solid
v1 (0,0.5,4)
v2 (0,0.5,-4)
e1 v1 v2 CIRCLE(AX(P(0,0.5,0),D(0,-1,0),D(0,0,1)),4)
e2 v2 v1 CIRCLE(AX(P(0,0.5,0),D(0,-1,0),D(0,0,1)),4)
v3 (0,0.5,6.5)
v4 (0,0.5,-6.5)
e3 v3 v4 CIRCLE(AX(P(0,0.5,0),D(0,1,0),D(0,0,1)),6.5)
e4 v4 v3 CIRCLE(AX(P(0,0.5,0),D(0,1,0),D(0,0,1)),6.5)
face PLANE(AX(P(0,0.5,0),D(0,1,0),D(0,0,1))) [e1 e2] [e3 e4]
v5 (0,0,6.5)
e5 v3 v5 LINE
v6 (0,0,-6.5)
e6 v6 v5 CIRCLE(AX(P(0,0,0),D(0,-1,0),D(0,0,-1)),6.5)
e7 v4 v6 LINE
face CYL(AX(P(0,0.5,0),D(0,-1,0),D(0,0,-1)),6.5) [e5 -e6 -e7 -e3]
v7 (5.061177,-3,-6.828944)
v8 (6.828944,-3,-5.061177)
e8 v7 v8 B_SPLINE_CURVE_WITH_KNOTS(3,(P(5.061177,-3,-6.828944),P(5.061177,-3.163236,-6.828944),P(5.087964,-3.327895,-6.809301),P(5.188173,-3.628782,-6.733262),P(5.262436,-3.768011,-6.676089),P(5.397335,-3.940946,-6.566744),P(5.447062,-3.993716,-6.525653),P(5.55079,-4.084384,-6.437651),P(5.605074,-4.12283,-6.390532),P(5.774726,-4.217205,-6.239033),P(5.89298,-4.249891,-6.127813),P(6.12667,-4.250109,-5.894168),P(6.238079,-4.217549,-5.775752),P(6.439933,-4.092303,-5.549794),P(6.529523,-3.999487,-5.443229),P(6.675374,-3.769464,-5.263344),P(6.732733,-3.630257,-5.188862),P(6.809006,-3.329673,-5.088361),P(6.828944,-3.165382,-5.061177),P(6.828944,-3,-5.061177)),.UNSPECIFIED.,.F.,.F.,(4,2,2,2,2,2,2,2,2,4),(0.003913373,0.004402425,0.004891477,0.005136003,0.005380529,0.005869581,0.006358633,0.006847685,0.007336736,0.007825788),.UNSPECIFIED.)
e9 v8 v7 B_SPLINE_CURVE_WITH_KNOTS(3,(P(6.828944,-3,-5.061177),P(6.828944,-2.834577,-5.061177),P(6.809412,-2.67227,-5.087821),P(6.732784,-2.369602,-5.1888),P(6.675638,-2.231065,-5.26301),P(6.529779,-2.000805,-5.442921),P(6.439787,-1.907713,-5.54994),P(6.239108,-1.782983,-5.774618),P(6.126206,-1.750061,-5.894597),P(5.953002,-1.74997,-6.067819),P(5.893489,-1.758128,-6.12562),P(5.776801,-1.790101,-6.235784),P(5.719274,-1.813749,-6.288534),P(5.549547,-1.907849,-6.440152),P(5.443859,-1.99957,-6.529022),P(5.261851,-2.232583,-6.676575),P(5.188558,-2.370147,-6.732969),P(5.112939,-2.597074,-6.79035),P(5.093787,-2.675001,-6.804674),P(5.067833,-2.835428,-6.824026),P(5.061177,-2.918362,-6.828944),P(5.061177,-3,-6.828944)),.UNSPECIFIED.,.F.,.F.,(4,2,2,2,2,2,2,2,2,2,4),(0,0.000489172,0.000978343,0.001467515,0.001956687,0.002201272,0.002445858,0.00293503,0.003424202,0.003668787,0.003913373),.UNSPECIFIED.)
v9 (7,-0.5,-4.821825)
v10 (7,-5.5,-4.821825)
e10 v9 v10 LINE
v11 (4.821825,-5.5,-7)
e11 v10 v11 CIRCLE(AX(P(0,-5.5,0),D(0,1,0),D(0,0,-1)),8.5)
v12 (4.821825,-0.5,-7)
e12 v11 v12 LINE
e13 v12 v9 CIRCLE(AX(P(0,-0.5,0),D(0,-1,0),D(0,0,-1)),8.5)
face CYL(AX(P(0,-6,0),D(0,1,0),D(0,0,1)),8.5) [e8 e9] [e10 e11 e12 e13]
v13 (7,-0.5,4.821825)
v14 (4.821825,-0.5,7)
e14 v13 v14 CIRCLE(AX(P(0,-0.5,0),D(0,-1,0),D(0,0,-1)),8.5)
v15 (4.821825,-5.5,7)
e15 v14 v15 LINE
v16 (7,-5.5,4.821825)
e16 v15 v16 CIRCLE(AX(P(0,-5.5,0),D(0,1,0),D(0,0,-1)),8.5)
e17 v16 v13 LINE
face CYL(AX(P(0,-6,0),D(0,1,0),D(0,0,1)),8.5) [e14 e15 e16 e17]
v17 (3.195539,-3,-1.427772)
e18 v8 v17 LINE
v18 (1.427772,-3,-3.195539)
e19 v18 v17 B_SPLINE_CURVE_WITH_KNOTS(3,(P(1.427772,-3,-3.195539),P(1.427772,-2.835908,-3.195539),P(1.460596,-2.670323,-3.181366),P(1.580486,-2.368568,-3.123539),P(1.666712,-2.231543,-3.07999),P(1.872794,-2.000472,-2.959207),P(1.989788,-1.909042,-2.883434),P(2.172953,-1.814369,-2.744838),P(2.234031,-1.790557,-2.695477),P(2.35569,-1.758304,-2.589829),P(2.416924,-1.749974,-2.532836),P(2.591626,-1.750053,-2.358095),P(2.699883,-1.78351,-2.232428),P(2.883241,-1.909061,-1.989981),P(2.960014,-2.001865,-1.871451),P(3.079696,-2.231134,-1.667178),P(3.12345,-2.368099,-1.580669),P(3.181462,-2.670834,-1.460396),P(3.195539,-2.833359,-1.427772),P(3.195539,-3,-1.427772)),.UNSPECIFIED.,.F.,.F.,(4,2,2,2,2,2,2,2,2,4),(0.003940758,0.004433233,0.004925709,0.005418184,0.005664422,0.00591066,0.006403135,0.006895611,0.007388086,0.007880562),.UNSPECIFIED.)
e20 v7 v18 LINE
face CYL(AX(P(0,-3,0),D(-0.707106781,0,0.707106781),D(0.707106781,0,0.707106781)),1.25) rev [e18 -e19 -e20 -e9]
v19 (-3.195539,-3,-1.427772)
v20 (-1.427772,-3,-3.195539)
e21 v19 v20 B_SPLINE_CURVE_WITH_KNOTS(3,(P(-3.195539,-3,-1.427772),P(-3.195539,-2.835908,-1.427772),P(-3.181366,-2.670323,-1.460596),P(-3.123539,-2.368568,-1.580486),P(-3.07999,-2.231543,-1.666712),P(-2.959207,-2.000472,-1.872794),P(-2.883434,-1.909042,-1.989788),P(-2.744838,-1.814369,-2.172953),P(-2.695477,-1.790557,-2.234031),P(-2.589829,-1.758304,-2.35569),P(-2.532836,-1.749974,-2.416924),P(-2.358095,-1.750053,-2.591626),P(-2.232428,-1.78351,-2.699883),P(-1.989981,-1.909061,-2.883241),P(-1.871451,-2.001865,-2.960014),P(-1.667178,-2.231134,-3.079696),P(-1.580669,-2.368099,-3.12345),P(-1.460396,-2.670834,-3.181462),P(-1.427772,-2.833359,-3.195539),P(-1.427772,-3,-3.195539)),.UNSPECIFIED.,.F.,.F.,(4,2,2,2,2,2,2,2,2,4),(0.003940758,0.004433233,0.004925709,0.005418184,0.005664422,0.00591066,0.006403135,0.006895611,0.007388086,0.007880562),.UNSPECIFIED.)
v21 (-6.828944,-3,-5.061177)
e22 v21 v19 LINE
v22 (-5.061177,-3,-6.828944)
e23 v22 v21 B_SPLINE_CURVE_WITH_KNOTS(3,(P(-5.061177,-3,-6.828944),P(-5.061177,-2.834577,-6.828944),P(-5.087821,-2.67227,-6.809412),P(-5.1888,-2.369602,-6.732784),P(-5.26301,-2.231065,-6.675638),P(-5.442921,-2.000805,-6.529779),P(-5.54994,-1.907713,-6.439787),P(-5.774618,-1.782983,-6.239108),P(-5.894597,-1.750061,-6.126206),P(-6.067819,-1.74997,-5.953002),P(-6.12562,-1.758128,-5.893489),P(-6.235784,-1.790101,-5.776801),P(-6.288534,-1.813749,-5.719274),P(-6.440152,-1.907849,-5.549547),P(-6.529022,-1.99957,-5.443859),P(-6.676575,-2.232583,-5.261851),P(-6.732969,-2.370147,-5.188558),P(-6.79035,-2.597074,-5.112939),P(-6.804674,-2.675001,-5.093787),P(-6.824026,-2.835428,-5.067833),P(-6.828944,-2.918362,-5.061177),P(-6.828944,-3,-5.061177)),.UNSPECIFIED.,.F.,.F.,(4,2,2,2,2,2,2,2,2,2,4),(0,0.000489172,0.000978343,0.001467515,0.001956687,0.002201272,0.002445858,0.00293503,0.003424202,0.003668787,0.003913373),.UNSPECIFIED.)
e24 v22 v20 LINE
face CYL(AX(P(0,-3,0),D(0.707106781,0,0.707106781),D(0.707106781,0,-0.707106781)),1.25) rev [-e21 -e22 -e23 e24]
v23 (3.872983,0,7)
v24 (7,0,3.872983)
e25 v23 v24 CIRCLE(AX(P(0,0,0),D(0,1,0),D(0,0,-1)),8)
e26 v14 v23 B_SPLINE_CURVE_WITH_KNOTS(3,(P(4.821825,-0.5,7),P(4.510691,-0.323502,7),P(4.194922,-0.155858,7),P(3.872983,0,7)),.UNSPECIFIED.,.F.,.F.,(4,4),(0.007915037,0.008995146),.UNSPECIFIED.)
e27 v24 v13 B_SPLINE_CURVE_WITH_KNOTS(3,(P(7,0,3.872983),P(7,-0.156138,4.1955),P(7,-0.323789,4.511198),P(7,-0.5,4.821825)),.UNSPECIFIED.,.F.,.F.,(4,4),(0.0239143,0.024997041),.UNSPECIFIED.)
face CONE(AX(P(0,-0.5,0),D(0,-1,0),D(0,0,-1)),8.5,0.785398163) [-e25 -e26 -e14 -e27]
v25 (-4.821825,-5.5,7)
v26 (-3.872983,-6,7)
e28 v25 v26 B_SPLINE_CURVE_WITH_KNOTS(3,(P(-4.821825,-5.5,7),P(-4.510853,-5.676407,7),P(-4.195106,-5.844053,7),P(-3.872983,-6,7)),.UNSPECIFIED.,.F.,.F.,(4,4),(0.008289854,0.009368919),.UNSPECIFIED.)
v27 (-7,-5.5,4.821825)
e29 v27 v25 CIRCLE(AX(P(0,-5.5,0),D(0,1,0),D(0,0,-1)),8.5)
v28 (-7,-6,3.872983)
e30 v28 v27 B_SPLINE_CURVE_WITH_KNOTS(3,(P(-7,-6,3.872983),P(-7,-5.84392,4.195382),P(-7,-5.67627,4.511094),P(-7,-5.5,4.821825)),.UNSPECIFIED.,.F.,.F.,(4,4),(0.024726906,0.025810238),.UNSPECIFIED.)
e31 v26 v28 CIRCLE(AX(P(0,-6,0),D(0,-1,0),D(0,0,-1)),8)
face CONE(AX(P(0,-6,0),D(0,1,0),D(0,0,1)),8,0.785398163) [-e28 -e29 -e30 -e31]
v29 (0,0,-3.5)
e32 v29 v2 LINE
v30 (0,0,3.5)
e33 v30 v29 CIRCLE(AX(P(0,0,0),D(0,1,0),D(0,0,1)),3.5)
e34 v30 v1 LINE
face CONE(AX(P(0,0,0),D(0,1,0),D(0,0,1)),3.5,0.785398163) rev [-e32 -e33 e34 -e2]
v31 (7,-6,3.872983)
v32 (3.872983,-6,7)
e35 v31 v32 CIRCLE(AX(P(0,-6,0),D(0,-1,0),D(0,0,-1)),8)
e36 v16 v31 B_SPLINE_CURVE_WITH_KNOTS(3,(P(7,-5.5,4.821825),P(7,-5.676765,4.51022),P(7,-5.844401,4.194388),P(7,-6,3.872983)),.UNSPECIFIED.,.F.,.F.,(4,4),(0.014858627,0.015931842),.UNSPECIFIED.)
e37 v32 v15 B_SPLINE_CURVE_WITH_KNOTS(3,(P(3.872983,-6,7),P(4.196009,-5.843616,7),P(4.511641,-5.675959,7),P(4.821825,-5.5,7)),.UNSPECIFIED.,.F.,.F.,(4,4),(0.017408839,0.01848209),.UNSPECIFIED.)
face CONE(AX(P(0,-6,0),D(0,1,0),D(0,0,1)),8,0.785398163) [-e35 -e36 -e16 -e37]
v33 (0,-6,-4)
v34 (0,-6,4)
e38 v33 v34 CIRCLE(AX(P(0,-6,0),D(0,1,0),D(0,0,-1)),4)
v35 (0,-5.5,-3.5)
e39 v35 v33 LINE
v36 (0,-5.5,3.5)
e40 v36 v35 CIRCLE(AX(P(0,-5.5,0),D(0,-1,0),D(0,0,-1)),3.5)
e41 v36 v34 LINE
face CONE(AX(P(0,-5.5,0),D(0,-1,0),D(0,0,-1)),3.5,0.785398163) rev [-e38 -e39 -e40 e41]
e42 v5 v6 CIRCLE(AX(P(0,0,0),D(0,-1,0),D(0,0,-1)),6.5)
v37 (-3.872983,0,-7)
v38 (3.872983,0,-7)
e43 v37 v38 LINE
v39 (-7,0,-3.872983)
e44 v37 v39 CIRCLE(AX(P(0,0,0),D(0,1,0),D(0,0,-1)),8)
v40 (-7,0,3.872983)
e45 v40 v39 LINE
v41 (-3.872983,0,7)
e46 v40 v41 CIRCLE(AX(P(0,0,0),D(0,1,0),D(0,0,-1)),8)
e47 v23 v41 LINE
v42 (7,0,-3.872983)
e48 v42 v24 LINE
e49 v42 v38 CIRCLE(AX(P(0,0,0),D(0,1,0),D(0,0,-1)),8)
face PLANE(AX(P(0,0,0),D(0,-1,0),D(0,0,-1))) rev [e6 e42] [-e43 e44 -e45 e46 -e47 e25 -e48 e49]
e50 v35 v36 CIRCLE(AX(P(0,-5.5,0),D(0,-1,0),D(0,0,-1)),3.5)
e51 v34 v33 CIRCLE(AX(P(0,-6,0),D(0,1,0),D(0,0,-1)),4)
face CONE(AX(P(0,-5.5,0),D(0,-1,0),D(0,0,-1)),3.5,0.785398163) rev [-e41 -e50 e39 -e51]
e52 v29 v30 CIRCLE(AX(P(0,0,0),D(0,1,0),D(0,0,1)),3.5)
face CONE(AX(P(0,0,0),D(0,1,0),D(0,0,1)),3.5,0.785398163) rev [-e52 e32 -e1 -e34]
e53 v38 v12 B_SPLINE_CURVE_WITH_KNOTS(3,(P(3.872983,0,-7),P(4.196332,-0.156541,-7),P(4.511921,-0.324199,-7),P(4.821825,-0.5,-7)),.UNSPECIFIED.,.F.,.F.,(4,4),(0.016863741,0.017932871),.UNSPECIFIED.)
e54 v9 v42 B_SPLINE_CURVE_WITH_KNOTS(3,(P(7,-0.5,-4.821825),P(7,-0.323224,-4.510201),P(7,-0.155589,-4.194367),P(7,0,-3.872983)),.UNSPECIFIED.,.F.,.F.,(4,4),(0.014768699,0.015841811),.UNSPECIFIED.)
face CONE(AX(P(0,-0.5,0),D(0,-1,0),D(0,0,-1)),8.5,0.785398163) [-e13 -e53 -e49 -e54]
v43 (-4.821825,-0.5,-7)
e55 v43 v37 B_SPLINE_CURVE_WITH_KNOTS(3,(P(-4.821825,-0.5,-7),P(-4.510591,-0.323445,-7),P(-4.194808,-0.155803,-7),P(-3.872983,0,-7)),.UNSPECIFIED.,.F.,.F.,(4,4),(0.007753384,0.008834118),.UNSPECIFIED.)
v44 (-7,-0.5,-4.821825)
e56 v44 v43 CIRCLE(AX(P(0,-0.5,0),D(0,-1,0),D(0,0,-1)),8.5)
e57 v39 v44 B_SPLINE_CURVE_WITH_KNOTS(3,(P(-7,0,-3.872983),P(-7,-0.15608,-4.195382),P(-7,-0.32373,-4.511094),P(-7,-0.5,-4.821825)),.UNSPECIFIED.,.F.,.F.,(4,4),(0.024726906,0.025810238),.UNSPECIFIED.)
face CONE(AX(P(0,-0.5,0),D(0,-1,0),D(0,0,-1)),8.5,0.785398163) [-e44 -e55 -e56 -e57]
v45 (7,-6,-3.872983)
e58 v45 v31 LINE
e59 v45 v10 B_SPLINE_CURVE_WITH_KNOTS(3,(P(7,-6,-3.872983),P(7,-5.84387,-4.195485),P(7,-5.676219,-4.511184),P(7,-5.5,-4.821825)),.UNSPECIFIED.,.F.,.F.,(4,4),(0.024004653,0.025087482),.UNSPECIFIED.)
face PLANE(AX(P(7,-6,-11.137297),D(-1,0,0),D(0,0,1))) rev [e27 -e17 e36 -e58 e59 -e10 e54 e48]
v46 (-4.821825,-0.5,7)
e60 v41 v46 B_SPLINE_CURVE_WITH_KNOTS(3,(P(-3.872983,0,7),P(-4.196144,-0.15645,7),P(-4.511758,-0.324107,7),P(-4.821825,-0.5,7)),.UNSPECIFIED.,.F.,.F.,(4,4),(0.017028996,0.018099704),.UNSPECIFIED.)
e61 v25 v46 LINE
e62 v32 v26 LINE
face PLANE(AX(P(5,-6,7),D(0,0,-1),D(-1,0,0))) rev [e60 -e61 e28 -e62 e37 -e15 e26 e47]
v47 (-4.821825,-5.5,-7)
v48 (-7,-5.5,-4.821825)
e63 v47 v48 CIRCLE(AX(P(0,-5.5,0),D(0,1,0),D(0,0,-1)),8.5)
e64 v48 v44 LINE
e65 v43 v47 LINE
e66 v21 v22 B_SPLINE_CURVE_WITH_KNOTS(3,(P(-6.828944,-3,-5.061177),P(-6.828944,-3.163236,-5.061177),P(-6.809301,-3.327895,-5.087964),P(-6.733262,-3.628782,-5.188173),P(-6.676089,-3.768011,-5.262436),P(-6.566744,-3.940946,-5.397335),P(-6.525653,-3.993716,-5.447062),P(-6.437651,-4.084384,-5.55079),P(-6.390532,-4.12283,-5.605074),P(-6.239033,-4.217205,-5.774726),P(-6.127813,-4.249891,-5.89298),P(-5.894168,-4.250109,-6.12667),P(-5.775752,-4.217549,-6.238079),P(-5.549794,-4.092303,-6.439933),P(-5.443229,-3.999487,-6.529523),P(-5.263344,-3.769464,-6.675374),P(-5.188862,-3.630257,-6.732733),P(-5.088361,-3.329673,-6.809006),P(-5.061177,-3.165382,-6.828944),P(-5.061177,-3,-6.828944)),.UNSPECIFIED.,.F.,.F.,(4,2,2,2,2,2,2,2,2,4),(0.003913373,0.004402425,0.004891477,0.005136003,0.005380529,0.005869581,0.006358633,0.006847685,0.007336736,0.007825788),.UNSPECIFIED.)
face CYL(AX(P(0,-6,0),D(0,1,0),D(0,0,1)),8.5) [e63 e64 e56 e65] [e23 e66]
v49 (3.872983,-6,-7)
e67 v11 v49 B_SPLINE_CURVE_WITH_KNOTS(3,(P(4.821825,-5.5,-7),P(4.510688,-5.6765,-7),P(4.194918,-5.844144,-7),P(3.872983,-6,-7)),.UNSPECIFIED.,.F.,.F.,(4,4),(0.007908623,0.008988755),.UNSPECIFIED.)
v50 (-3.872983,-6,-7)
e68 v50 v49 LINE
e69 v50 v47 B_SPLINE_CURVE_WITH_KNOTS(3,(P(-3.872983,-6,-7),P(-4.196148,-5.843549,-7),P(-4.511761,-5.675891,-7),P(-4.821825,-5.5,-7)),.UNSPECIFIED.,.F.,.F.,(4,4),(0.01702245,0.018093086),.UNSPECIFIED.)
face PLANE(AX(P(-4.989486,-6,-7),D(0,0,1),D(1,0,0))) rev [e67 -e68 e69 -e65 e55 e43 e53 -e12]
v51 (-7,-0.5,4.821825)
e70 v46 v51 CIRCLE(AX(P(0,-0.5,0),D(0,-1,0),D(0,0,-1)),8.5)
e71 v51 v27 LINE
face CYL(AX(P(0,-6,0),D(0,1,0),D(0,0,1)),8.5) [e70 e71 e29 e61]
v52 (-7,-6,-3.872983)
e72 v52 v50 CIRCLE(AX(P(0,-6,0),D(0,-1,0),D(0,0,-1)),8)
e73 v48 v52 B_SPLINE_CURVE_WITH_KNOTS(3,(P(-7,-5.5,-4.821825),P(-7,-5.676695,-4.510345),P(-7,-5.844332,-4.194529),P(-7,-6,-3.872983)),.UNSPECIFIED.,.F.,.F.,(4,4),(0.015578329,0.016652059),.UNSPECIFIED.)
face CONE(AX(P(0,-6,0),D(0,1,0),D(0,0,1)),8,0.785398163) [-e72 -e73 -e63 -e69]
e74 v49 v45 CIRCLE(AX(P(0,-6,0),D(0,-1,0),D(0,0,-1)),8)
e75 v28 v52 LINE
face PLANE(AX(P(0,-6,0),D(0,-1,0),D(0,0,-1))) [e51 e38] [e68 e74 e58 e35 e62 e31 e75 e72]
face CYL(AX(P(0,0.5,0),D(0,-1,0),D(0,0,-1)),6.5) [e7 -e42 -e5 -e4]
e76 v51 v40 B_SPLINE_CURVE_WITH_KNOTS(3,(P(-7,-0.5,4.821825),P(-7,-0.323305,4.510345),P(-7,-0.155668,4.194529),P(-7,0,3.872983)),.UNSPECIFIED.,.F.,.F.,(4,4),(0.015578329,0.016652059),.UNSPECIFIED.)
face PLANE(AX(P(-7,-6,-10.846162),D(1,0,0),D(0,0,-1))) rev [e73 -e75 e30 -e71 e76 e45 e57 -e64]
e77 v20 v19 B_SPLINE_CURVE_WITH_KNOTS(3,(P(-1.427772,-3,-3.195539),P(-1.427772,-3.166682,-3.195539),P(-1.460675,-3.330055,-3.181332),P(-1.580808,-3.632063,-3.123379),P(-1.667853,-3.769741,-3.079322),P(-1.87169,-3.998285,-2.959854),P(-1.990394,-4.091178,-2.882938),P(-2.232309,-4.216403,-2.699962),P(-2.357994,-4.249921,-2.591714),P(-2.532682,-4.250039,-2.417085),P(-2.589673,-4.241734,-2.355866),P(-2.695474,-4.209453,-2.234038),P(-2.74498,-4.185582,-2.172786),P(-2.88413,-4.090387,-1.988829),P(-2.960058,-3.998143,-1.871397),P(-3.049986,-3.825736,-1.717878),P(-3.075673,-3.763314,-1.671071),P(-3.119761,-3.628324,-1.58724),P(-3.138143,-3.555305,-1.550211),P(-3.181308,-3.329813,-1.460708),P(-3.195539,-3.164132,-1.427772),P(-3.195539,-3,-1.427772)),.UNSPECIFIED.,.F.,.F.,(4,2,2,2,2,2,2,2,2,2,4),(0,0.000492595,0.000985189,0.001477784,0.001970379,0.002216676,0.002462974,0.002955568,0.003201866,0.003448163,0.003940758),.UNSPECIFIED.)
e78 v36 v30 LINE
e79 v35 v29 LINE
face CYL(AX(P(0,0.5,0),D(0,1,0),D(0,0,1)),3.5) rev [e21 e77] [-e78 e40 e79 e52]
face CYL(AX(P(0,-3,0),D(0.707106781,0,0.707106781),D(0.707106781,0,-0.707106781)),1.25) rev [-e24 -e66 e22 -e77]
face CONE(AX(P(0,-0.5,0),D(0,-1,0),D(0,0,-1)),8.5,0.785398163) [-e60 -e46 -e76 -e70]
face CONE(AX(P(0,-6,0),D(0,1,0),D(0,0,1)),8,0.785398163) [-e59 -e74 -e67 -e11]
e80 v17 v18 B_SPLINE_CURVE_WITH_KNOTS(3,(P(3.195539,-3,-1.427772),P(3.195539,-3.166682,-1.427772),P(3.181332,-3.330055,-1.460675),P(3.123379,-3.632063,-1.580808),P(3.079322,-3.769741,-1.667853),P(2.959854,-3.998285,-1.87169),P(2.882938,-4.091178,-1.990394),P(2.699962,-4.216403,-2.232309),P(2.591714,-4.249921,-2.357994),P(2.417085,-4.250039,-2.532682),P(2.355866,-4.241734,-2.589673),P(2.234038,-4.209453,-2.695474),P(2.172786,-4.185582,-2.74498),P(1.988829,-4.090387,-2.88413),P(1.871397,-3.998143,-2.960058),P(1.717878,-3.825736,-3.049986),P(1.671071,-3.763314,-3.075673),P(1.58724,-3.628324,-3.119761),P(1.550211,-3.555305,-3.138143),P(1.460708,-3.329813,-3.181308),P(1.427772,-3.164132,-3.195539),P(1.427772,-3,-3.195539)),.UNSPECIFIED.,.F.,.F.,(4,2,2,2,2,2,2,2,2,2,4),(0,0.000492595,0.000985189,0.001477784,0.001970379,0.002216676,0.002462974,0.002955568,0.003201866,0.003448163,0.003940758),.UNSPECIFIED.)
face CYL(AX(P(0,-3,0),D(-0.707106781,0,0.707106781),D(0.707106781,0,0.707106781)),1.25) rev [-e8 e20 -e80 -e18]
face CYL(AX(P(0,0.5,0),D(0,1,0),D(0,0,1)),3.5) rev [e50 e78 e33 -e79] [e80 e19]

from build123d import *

# Parameters (mm, degrees)
SKETCH1_R                 = 6.5
BOSS_EXTRUDE1_DEPTH       = 0.5
SKETCH3_R                 = 8.5
BOSS_EXTRUDE3_DEPTH       = 6
CHAMFER2_SIZE             = 0.5
SKETCH4_W                 = 4.01520781
SKETCH4_H                 = 18.659876277
SKETCH4_W_2               = 10.097066699
SKETCH4_H_2               = 2.598075642
SKETCH4_W_3               = 5.358269855
SKETCH4_H_3               = 23.485379118
SKETCH4_W_4               = 10.284722044
SKETCH4_H_4               = 2.952358684
CUT_EXTRUDE3_DEPTH        = 14.435028843
M8X1_0_TAPPED_HOLE1_D     = 7
M8X1_0_TAPPED_HOLE1_DEPTH = 19
M8X1_0_TAPPED_HOLE1_TIP   = 2.103012167
SKETCH7_W                 = 1.25
SKETCH7_H                 = 9.899494937
CHAMFER3_SIZE             = 0.5
CIRPATTERN1_COUNT         = 2
CIRPATTERN1_ANGLE         = 90


with BuildPart() as part:
    # Sketch1 → Boss-Extrude1 (new body)
    with BuildSketch(Plane(origin=(0, 0, 0), x_dir=(1, 0, 0), z_dir=(0, 1, 0))):
        with Locations(Location((0, 0, 0), (0, 0, 270))):
            Circle(SKETCH1_R)
    extrude(amount=BOSS_EXTRUDE1_DEPTH)

    # Sketch3 → Boss-Extrude3 (add)
    with BuildSketch(Plane.XZ):
        with Locations(Location((0, 0, 0), (0, 0, 270))):
            Circle(SKETCH3_R)
    extrude(amount=BOSS_EXTRUDE3_DEPTH)

    # Chamfer2
    chamfer2_edges = [part.edges().sort_by_distance(p)[0] for p in [
        (0, 0, 8.5),
        (0, -6, 8.5),
    ]]
    chamfer(chamfer2_edges, length=CHAMFER2_SIZE)

    # Sketch4 → Cut-Extrude3 (cut, through all)
    with BuildSketch(Plane(origin=(0, 0, 0), x_dir=(1, 0, 0), z_dir=(0, 1, 0))):
        with Locations((-9.007603905, 1.516224116)):
            Rectangle(SKETCH4_W, SKETCH4_H)
        with Locations((0.059047173, 8.299037821)):
            Rectangle(SKETCH4_W_2, SKETCH4_H_2)
        with Locations((9.679134928, -0.60539293)):
            Rectangle(SKETCH4_W_3, SKETCH4_H_3)
        with Locations((-0.142361022, -8.476179342)):
            Rectangle(SKETCH4_W_4, SKETCH4_H_4)
    extrude(amount=-CUT_EXTRUDE3_DEPTH, mode=Mode.SUBTRACT)

    # M8x1.0 Tapped Hole1
    with Locations(Plane(origin=(0, 0.5, 0), x_dir=(-1, 0, 0), z_dir=(0, 1, 0))):
        with Locations((0, 0)):
            Hole(M8X1_0_TAPPED_HOLE1_D / 2, depth=M8X1_0_TAPPED_HOLE1_DEPTH)
            with Locations((0, 0, -(M8X1_0_TAPPED_HOLE1_DEPTH + M8X1_0_TAPPED_HOLE1_TIP / 2))):  # 118° drill point
                Cone(0, M8X1_0_TAPPED_HOLE1_D / 2, M8X1_0_TAPPED_HOLE1_TIP, mode=Mode.SUBTRACT)

    # Sketch7 → M3 Tapped Hole1 (revolve, cut)
    with BuildSketch(Plane(origin=(0, -3, 0), x_dir=(0.7071067811865488, 0, 0.7071067811865464), z_dir=(0, 1, 0))):
        with Locations((0.625, 4.949747469)):
            Rectangle(SKETCH7_W, SKETCH7_H)
    m3_tapped_hole1 = revolve(axis=Axis((-4.490128061, -3, 4.490128061), (0.7071067811865464, 0, -0.7071067811865487)), mode=Mode.SUBTRACT)

    # Chamfer3
    chamfer3_edges = [part.edges().sort_by_distance(p)[0] for p in [
        (-3.5, -6, 0),
        (-3.5, 0.5, 0),
    ]]
    chamfer(chamfer3_edges, length=CHAMFER3_SIZE)

    # CirPattern1: M3 Tapped Hole1 ×2 about axis
    cirpattern1_axis = Axis((0, 0.5, 0), (0, 1, 0))
    for i in range(1, CIRPATTERN1_COUNT):
        add(m3_tapped_hole1.rotate(cirpattern1_axis, i * CIRPATTERN1_ANGLE / (CIRPATTERN1_COUNT - 1)), mode=Mode.SUBTRACT)


solid = part.part
